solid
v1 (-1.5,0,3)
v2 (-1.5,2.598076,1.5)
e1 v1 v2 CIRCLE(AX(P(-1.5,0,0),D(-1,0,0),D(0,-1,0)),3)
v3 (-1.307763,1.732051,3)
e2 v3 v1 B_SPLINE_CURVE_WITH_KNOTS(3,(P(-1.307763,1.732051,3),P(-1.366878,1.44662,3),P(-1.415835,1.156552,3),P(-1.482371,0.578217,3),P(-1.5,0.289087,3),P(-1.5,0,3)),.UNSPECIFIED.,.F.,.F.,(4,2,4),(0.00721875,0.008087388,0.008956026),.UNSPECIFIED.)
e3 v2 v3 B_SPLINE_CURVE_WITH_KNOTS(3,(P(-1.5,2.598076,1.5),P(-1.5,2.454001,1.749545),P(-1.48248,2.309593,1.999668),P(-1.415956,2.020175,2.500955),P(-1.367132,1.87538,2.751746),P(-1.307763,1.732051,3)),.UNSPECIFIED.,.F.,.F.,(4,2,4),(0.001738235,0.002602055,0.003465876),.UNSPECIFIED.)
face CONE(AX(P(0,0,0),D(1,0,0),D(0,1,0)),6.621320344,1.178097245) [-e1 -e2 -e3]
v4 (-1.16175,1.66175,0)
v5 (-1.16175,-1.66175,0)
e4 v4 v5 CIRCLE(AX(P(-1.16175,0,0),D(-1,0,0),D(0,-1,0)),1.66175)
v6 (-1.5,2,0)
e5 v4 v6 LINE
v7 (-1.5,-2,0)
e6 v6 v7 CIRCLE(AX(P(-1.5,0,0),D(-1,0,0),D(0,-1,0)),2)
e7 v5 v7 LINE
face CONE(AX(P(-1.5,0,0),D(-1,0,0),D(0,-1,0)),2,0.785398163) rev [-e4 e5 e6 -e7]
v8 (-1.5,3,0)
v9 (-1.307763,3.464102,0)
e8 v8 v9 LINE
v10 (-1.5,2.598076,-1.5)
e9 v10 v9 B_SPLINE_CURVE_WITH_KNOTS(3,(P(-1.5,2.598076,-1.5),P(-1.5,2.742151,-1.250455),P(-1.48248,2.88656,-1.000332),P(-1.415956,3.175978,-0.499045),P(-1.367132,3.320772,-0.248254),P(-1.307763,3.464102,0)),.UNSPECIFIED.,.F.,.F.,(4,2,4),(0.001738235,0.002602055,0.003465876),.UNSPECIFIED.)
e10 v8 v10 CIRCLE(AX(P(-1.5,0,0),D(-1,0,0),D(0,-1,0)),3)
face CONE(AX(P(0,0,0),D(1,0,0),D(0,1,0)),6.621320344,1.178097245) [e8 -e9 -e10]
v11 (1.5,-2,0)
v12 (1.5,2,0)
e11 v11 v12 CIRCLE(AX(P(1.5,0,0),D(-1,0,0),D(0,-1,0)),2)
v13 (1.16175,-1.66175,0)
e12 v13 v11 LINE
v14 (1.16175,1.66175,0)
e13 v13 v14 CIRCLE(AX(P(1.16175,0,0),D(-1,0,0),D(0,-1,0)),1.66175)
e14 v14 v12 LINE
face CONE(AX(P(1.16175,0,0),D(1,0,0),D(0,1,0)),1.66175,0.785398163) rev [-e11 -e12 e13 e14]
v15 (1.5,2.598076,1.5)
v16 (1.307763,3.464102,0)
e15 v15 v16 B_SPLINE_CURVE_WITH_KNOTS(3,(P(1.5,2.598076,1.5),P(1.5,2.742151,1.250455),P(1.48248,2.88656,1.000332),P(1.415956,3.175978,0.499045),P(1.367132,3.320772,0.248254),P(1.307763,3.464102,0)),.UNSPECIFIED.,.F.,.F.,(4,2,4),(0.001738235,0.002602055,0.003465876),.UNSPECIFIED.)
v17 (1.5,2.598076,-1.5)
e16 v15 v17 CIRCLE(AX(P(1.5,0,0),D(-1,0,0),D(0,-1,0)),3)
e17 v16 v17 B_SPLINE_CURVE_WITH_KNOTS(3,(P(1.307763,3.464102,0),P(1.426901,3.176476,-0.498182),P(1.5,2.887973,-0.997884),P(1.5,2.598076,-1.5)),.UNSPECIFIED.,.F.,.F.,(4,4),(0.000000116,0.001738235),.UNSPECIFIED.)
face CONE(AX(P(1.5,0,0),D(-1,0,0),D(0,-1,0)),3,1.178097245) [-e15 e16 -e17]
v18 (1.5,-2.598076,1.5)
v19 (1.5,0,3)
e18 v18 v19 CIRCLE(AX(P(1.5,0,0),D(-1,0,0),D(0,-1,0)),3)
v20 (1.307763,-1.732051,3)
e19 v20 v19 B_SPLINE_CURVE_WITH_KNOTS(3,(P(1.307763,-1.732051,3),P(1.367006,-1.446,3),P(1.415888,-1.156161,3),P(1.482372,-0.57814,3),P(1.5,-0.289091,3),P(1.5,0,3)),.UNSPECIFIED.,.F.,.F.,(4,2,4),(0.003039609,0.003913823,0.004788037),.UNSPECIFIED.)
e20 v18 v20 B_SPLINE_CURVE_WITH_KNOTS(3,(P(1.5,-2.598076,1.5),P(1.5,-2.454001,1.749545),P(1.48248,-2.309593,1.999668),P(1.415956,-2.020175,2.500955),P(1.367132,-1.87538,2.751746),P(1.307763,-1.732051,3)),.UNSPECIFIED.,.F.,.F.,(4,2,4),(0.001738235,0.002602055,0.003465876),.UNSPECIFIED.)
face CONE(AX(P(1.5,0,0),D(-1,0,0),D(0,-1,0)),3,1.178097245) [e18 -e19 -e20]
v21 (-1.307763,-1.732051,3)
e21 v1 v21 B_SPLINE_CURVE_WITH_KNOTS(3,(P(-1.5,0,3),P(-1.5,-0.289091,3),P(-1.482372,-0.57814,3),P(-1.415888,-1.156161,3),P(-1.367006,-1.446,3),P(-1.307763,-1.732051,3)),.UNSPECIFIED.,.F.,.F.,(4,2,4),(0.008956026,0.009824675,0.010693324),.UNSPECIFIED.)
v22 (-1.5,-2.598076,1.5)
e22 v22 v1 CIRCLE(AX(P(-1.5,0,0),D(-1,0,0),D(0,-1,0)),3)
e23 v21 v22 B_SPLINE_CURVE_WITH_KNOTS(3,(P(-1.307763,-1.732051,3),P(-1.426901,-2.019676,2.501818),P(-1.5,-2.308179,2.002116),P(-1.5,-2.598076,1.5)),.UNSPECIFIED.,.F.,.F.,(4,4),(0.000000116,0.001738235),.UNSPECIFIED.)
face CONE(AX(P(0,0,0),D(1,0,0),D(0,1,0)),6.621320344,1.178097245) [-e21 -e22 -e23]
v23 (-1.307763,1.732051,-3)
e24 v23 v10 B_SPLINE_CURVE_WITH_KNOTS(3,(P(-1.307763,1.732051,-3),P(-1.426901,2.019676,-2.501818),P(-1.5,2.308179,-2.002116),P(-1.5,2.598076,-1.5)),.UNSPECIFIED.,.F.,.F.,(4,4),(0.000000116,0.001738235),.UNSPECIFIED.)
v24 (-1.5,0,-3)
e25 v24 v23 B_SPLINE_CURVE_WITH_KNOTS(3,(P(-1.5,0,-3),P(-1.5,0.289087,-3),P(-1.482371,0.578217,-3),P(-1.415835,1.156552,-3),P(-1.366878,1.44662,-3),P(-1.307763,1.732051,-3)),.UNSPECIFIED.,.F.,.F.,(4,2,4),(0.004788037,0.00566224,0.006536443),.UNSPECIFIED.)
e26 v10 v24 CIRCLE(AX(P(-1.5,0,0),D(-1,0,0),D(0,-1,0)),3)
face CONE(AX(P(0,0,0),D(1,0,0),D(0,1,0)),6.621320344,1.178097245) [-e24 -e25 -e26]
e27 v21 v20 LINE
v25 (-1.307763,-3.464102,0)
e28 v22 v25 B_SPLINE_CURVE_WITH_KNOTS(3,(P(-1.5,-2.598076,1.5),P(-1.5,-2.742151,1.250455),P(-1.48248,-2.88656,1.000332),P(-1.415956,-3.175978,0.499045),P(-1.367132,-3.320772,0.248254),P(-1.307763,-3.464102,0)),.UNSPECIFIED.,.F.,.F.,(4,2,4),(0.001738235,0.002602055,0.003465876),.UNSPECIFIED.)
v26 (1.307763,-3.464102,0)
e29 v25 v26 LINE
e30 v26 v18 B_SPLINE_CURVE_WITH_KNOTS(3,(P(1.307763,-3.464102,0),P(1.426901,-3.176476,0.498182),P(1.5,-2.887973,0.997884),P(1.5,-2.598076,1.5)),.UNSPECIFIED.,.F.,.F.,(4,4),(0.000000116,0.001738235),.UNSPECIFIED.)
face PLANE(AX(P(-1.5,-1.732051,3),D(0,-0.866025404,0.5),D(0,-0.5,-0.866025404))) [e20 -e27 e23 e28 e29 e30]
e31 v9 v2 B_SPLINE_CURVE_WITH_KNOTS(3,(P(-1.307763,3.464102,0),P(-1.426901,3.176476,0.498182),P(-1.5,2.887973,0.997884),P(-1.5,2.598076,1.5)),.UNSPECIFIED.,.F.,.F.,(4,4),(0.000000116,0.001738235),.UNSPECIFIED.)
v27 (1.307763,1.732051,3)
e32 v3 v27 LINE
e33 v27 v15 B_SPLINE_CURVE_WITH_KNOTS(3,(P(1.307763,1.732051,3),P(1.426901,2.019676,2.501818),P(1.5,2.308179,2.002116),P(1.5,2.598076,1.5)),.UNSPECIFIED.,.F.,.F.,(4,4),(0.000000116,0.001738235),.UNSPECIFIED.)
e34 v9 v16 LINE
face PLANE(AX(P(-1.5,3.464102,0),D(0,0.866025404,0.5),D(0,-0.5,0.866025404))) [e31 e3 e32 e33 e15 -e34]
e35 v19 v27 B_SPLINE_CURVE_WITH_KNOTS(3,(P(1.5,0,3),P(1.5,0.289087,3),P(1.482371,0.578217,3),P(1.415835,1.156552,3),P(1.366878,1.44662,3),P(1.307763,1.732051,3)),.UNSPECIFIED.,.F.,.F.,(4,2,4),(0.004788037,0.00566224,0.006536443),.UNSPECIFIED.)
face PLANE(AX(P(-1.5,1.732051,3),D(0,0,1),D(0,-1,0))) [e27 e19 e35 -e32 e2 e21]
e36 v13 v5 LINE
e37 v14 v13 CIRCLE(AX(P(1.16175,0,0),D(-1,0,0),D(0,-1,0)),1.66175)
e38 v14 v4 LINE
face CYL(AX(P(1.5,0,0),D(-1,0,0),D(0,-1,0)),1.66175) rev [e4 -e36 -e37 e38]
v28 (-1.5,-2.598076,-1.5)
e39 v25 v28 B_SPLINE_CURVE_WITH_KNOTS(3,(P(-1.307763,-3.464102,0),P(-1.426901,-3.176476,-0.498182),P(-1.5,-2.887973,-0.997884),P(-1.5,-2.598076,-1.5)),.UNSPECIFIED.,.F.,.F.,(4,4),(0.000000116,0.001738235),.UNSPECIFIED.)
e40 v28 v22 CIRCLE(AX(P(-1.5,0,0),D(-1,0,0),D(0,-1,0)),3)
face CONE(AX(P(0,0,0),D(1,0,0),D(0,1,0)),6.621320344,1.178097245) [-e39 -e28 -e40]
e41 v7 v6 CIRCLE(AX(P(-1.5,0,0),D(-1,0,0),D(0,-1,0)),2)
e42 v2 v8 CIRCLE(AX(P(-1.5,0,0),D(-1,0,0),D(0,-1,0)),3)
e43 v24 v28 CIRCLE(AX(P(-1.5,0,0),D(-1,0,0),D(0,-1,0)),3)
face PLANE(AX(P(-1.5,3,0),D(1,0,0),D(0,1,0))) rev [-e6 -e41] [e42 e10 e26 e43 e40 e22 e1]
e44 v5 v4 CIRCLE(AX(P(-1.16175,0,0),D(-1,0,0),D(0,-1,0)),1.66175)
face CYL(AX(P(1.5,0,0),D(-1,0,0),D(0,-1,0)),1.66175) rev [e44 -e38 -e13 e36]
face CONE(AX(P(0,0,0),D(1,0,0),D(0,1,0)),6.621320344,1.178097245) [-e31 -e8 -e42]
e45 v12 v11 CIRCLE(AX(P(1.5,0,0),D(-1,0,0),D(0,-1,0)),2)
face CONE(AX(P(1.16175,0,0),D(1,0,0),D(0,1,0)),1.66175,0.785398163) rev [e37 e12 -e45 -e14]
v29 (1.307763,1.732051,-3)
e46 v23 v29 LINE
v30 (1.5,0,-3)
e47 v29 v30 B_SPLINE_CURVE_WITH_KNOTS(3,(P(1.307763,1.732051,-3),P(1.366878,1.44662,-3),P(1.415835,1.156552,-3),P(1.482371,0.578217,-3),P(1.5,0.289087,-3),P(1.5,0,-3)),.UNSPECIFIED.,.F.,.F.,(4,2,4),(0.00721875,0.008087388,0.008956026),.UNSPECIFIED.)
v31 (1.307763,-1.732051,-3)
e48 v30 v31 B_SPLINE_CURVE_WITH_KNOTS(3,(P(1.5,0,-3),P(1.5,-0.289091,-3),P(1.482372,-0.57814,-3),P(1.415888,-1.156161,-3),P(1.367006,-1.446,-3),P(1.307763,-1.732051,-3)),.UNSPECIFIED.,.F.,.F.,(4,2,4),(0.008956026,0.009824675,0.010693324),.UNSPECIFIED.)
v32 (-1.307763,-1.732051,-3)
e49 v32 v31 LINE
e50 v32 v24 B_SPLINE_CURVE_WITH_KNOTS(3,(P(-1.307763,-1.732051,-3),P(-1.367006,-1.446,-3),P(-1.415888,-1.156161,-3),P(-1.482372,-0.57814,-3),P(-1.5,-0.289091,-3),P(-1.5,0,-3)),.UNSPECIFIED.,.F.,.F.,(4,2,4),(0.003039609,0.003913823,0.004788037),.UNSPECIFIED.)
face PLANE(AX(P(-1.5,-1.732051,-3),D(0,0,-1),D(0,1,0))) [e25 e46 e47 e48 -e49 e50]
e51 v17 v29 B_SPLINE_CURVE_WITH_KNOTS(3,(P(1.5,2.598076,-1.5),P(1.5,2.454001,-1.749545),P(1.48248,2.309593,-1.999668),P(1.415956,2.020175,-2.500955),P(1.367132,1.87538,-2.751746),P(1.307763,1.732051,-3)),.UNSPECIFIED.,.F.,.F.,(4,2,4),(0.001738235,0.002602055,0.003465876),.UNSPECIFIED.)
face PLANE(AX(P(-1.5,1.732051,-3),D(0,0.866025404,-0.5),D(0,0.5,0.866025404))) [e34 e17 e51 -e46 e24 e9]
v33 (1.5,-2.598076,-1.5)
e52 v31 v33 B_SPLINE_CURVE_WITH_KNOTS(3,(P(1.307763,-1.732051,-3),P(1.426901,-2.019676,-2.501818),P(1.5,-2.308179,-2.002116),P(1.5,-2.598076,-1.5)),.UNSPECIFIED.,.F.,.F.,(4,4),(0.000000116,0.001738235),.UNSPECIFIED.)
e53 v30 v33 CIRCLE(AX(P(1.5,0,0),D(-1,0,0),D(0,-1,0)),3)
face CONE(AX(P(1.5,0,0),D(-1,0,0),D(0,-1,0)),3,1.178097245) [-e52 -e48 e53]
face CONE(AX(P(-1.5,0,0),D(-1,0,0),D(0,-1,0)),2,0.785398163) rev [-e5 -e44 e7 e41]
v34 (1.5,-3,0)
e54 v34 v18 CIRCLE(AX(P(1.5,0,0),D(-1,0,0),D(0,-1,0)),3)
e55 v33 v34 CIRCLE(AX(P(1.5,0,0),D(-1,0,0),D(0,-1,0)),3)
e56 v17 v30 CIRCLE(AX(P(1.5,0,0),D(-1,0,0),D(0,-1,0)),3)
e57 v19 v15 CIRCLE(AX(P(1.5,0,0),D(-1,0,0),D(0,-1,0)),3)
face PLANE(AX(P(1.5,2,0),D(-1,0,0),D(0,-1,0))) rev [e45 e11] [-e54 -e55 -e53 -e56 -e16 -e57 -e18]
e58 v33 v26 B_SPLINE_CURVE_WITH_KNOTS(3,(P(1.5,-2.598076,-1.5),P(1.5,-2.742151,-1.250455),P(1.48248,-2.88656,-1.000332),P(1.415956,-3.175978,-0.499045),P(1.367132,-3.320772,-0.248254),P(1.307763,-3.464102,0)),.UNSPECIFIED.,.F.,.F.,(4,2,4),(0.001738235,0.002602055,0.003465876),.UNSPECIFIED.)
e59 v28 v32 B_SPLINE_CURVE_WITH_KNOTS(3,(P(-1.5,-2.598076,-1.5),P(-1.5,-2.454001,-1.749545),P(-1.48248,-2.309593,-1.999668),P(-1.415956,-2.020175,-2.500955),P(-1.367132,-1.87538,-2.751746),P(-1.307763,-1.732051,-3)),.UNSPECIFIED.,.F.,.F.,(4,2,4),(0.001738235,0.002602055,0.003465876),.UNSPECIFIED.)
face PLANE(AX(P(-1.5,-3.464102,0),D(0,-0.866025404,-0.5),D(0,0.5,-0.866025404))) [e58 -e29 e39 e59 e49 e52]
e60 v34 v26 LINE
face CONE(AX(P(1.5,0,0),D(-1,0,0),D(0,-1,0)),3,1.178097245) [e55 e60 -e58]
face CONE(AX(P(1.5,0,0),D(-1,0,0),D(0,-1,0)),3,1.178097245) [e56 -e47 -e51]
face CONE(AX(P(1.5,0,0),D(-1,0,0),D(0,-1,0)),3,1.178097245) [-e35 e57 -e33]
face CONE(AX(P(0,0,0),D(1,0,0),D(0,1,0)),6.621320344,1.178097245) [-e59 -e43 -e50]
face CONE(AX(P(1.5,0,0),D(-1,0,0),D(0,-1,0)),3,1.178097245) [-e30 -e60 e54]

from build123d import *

# Parameters (mm, degrees)
CUT_EXTRUDE_1_DEPTH      = 3
CUT_EXTRUDE_1_DEPTH_BACK = 3
SKETCH_2_R               = 45
SCALE_1_SCALE            = 0.5


with BuildPart() as part:
    # 草图1 → 旋转1 (revolve)
    with BuildSketch(Plane.XY, mode=Mode.PRIVATE) as revolve_1_sk:
        Polygon((-3, 6), (-3, 4), (-2.3235, 3.3235), (2.3235, 3.3235), (3, 4), (3, 6), (0, 13.242640687), align=None)
    revolve(revolve_1_sk.sketch.rotate(Axis((3, 0, 0), (-1, 0, 0)), 180), axis=Axis((3, 0, 0), (-1, 0, 0)))

    # 草图2 → 切除-拉伸1 (cut, two sides: drawn at the far end of the back side and taken through both)
    with BuildSketch(Plane(origin=(0, 0, 0), x_dir=(0, 0, -1), z_dir=(1, 0, 0)).offset(-CUT_EXTRUDE_1_DEPTH_BACK)):
        Circle(SKETCH_2_R)
        Polygon((-6, -3.464101615), (0, -6.92820323), (6, -3.464101615), (6, 3.464101615), (0, 6.92820323), (-6, 3.464101615), align=None, mode=Mode.SUBTRACT)
    extrude(amount=CUT_EXTRUDE_1_DEPTH + CUT_EXTRUDE_1_DEPTH_BACK, mode=Mode.SUBTRACT)


with BuildPart() as part_1:
    # 缩放比例1: scaled about (0, 1e-09, 0)
    add(part.part.scale(SCALE_1_SCALE).moved(Location((0, 1e-09, 0))))


solid = part_1.part
